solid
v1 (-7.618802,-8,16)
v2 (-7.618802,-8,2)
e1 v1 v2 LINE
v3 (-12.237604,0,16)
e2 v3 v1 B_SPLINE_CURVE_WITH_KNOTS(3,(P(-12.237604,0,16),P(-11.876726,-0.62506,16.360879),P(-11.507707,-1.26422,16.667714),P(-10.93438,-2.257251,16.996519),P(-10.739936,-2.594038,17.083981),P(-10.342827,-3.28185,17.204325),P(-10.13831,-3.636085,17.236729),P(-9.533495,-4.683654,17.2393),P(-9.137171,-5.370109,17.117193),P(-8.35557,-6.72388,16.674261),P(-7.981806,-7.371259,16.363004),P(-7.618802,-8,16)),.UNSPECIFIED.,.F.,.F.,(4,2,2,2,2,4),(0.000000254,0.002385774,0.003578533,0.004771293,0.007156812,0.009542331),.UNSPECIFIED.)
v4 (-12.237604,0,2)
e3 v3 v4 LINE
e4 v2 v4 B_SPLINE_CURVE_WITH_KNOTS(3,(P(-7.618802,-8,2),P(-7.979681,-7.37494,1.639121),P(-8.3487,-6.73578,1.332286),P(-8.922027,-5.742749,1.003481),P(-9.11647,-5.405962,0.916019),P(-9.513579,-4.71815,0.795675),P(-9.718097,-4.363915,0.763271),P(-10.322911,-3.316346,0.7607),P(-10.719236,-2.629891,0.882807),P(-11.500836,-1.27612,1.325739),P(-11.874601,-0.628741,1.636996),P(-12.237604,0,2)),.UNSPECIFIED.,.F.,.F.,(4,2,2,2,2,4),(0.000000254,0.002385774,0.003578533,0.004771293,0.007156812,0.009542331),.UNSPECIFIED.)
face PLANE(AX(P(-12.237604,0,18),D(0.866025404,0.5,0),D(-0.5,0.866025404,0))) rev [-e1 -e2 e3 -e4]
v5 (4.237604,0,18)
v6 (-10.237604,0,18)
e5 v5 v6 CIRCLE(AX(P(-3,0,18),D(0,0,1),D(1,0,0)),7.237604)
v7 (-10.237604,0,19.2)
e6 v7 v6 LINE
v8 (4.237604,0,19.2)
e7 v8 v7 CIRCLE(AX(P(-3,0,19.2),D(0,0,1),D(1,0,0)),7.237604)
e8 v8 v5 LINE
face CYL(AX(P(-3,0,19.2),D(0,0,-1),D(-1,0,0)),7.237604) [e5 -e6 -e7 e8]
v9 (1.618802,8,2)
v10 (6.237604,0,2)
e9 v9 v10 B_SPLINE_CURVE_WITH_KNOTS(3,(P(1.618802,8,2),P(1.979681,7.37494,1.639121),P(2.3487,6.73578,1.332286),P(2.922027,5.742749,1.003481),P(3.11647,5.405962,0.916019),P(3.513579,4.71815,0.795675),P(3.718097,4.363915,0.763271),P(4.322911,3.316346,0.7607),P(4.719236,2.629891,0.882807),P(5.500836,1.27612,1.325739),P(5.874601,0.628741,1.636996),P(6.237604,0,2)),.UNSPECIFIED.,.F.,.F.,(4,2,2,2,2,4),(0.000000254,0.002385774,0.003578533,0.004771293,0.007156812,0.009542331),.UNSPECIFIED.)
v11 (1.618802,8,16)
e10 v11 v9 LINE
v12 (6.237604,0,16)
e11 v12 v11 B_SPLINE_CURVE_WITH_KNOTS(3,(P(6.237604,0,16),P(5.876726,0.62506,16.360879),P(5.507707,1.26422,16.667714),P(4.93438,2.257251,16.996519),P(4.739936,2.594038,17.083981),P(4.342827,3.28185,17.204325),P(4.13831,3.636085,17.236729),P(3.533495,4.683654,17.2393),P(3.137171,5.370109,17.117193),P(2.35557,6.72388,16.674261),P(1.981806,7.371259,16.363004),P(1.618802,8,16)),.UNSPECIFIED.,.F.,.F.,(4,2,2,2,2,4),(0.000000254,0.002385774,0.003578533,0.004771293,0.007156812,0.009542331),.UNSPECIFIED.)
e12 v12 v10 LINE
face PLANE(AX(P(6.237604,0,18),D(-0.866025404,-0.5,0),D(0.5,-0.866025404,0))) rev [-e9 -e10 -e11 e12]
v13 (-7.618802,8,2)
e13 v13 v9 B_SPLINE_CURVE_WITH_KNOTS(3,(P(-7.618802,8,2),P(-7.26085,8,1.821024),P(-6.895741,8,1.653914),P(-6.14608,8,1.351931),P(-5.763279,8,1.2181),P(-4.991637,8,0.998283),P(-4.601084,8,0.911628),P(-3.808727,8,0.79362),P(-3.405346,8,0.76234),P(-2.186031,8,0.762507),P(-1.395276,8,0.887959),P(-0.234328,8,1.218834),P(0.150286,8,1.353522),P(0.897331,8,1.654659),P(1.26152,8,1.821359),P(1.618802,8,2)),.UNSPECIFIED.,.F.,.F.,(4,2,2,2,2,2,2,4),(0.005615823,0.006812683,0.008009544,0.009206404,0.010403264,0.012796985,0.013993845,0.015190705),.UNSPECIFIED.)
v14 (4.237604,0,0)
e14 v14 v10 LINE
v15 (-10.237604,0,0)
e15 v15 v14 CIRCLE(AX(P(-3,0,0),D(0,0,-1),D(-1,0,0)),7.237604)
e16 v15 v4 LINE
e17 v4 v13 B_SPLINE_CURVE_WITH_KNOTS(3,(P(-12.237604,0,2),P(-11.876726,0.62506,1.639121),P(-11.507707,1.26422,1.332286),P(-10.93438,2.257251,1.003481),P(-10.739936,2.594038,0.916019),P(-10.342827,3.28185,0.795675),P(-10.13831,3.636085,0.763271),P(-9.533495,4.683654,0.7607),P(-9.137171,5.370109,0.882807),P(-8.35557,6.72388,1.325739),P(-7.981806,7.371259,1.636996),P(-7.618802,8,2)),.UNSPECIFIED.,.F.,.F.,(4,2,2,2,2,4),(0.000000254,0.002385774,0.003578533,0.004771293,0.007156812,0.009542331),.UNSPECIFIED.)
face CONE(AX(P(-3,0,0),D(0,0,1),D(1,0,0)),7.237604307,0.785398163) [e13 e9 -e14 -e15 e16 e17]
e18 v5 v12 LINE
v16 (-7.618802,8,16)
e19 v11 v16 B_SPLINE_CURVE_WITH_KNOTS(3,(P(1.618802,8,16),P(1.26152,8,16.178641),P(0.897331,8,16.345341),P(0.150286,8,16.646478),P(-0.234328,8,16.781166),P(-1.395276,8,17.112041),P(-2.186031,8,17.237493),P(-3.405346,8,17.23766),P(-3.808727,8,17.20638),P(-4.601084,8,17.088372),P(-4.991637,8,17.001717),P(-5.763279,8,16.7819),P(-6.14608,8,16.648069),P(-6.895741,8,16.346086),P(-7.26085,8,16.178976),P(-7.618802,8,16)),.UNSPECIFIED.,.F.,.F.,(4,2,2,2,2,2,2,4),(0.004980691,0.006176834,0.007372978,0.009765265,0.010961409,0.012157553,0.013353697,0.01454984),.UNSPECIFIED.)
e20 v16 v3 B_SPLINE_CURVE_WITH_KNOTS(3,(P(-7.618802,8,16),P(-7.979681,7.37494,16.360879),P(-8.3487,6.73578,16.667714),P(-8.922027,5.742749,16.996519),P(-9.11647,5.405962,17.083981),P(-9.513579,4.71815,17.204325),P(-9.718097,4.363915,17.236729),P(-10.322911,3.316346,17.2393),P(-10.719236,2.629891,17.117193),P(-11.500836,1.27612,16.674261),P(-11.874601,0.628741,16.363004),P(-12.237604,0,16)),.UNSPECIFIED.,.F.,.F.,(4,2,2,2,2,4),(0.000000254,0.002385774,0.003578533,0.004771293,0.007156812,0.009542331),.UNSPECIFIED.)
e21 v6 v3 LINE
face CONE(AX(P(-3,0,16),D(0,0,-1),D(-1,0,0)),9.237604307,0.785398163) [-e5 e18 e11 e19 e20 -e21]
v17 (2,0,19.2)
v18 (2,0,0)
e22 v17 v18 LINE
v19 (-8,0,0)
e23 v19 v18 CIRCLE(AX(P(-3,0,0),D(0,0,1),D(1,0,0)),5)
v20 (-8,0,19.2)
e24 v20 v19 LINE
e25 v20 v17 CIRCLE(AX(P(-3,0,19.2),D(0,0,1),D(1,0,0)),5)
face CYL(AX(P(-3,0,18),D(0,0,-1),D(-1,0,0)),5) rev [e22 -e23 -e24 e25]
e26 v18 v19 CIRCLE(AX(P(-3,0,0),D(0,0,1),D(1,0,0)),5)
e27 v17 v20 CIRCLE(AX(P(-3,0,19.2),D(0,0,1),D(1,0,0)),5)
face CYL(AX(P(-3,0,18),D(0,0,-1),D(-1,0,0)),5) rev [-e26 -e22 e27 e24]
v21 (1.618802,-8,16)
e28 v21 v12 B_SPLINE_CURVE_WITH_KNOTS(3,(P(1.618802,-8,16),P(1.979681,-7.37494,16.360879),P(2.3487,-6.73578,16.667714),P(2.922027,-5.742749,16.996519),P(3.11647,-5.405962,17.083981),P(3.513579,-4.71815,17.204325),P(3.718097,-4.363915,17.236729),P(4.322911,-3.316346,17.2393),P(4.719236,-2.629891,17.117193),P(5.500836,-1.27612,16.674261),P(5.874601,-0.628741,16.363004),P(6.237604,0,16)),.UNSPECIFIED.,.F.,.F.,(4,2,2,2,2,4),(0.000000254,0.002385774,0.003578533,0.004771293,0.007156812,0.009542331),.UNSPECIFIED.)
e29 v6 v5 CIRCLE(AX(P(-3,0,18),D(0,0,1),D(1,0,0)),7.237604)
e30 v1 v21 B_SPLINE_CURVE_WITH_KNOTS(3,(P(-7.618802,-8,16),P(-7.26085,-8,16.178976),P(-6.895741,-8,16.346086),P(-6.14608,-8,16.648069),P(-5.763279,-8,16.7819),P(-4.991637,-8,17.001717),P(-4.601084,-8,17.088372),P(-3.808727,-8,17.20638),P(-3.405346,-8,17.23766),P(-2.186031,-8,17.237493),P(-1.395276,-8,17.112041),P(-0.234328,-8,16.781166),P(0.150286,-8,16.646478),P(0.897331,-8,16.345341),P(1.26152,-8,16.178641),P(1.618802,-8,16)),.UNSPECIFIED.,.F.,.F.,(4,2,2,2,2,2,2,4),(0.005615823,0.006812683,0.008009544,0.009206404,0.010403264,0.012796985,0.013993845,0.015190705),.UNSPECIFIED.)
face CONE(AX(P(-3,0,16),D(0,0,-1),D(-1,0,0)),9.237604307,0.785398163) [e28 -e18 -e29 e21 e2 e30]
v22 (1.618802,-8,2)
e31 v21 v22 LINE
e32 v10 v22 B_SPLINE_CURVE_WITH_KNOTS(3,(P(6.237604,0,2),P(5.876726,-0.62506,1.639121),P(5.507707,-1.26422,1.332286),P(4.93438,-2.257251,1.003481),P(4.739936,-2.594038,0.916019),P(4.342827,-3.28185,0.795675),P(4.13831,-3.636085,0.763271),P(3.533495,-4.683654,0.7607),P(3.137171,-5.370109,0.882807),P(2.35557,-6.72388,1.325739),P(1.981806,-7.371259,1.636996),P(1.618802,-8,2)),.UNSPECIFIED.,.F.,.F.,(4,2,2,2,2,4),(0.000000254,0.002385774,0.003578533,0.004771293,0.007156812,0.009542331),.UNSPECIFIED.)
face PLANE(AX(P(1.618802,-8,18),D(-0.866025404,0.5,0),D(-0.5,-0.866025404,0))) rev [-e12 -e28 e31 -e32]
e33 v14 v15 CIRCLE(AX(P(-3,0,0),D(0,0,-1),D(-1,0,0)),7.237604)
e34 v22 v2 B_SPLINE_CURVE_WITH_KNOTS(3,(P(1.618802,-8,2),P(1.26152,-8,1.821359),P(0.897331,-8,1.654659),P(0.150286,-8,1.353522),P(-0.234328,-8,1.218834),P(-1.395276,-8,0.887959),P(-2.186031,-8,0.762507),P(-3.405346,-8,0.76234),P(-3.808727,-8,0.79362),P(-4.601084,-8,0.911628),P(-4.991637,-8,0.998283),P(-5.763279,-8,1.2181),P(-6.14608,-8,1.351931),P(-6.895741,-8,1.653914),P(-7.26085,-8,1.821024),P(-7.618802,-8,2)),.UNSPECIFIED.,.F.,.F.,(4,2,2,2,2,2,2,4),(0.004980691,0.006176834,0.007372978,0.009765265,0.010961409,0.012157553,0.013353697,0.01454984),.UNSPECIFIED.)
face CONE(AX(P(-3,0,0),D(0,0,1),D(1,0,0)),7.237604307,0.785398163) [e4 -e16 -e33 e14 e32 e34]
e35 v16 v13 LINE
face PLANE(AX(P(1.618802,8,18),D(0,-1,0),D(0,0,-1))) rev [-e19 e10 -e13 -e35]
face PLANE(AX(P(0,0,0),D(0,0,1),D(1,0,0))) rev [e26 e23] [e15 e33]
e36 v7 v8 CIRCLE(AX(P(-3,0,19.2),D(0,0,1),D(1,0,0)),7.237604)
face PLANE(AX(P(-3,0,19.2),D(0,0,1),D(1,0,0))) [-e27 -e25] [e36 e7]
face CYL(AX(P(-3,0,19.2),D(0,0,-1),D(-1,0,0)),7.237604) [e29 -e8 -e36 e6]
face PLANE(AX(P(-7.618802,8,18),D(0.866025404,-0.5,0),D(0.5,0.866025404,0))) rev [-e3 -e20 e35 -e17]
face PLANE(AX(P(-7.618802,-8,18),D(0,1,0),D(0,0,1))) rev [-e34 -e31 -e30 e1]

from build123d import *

# Parameters (mm, degrees)
SKETCH2_R           = 5
BOSS_EXTRUDE1_DEPTH = 18
SKETCH4_R           = 7.237604307
SKETCH4_R_2         = 5
BOSS_EXTRUDE2_DEPTH = 1.2


with BuildPart() as part:
    # Sketch2 → Boss-Extrude1 (new body)
    with BuildSketch(Plane.XY):
        Polygon((6.237604307, 0), (1.618802154, 8), (-7.618802154, 8), (-12.237604307, 0), (-7.618802154, -8), (1.618802154, -8), align=None)
        with Locations((-3, 0)):
            Circle(SKETCH2_R, mode=Mode.SUBTRACT)
    extrude(amount=BOSS_EXTRUDE1_DEPTH)

    # Sketch3 → Cut-Revolve1 (revolve, cut)
    with BuildSketch(Plane(origin=(0, 0, 0), x_dir=(1, 0, 0), z_dir=(0, 1, 0)), mode=Mode.PRIVATE) as cut_revolve1_sk:
        Polygon((6.237604307, -16), (4.237604307, -18), (6.237604307, -18), align=None)
    revolve(cut_revolve1_sk.sketch.rotate(Axis((-3, 0, 18), (0, 0, 1)), 180), axis=Axis((-3, 0, 18), (0, 0, 1)), mode=Mode.SUBTRACT)

    # Sketch4 → Boss-Extrude2 (add)
    with BuildSketch(Plane.XY.offset(18)):
        with Locations((-3, 0)):
            Circle(SKETCH4_R)
        with Locations((-3, 0)):
            Circle(SKETCH4_R_2, mode=Mode.SUBTRACT)
    extrude(amount=BOSS_EXTRUDE2_DEPTH)

    # Sketch5 → Cut-Revolve2 (revolve, cut)
    with BuildSketch(Plane(origin=(0, 0, 0), x_dir=(1, 0, 0), z_dir=(0, 1, 0))):
        Polygon((4.237604307, 0), (6.237604307, 0), (6.237604307, -2), align=None)
    revolve(axis=Axis((-3, 0, 0), (0, 0, 1)), mode=Mode.SUBTRACT)


solid = part.part
